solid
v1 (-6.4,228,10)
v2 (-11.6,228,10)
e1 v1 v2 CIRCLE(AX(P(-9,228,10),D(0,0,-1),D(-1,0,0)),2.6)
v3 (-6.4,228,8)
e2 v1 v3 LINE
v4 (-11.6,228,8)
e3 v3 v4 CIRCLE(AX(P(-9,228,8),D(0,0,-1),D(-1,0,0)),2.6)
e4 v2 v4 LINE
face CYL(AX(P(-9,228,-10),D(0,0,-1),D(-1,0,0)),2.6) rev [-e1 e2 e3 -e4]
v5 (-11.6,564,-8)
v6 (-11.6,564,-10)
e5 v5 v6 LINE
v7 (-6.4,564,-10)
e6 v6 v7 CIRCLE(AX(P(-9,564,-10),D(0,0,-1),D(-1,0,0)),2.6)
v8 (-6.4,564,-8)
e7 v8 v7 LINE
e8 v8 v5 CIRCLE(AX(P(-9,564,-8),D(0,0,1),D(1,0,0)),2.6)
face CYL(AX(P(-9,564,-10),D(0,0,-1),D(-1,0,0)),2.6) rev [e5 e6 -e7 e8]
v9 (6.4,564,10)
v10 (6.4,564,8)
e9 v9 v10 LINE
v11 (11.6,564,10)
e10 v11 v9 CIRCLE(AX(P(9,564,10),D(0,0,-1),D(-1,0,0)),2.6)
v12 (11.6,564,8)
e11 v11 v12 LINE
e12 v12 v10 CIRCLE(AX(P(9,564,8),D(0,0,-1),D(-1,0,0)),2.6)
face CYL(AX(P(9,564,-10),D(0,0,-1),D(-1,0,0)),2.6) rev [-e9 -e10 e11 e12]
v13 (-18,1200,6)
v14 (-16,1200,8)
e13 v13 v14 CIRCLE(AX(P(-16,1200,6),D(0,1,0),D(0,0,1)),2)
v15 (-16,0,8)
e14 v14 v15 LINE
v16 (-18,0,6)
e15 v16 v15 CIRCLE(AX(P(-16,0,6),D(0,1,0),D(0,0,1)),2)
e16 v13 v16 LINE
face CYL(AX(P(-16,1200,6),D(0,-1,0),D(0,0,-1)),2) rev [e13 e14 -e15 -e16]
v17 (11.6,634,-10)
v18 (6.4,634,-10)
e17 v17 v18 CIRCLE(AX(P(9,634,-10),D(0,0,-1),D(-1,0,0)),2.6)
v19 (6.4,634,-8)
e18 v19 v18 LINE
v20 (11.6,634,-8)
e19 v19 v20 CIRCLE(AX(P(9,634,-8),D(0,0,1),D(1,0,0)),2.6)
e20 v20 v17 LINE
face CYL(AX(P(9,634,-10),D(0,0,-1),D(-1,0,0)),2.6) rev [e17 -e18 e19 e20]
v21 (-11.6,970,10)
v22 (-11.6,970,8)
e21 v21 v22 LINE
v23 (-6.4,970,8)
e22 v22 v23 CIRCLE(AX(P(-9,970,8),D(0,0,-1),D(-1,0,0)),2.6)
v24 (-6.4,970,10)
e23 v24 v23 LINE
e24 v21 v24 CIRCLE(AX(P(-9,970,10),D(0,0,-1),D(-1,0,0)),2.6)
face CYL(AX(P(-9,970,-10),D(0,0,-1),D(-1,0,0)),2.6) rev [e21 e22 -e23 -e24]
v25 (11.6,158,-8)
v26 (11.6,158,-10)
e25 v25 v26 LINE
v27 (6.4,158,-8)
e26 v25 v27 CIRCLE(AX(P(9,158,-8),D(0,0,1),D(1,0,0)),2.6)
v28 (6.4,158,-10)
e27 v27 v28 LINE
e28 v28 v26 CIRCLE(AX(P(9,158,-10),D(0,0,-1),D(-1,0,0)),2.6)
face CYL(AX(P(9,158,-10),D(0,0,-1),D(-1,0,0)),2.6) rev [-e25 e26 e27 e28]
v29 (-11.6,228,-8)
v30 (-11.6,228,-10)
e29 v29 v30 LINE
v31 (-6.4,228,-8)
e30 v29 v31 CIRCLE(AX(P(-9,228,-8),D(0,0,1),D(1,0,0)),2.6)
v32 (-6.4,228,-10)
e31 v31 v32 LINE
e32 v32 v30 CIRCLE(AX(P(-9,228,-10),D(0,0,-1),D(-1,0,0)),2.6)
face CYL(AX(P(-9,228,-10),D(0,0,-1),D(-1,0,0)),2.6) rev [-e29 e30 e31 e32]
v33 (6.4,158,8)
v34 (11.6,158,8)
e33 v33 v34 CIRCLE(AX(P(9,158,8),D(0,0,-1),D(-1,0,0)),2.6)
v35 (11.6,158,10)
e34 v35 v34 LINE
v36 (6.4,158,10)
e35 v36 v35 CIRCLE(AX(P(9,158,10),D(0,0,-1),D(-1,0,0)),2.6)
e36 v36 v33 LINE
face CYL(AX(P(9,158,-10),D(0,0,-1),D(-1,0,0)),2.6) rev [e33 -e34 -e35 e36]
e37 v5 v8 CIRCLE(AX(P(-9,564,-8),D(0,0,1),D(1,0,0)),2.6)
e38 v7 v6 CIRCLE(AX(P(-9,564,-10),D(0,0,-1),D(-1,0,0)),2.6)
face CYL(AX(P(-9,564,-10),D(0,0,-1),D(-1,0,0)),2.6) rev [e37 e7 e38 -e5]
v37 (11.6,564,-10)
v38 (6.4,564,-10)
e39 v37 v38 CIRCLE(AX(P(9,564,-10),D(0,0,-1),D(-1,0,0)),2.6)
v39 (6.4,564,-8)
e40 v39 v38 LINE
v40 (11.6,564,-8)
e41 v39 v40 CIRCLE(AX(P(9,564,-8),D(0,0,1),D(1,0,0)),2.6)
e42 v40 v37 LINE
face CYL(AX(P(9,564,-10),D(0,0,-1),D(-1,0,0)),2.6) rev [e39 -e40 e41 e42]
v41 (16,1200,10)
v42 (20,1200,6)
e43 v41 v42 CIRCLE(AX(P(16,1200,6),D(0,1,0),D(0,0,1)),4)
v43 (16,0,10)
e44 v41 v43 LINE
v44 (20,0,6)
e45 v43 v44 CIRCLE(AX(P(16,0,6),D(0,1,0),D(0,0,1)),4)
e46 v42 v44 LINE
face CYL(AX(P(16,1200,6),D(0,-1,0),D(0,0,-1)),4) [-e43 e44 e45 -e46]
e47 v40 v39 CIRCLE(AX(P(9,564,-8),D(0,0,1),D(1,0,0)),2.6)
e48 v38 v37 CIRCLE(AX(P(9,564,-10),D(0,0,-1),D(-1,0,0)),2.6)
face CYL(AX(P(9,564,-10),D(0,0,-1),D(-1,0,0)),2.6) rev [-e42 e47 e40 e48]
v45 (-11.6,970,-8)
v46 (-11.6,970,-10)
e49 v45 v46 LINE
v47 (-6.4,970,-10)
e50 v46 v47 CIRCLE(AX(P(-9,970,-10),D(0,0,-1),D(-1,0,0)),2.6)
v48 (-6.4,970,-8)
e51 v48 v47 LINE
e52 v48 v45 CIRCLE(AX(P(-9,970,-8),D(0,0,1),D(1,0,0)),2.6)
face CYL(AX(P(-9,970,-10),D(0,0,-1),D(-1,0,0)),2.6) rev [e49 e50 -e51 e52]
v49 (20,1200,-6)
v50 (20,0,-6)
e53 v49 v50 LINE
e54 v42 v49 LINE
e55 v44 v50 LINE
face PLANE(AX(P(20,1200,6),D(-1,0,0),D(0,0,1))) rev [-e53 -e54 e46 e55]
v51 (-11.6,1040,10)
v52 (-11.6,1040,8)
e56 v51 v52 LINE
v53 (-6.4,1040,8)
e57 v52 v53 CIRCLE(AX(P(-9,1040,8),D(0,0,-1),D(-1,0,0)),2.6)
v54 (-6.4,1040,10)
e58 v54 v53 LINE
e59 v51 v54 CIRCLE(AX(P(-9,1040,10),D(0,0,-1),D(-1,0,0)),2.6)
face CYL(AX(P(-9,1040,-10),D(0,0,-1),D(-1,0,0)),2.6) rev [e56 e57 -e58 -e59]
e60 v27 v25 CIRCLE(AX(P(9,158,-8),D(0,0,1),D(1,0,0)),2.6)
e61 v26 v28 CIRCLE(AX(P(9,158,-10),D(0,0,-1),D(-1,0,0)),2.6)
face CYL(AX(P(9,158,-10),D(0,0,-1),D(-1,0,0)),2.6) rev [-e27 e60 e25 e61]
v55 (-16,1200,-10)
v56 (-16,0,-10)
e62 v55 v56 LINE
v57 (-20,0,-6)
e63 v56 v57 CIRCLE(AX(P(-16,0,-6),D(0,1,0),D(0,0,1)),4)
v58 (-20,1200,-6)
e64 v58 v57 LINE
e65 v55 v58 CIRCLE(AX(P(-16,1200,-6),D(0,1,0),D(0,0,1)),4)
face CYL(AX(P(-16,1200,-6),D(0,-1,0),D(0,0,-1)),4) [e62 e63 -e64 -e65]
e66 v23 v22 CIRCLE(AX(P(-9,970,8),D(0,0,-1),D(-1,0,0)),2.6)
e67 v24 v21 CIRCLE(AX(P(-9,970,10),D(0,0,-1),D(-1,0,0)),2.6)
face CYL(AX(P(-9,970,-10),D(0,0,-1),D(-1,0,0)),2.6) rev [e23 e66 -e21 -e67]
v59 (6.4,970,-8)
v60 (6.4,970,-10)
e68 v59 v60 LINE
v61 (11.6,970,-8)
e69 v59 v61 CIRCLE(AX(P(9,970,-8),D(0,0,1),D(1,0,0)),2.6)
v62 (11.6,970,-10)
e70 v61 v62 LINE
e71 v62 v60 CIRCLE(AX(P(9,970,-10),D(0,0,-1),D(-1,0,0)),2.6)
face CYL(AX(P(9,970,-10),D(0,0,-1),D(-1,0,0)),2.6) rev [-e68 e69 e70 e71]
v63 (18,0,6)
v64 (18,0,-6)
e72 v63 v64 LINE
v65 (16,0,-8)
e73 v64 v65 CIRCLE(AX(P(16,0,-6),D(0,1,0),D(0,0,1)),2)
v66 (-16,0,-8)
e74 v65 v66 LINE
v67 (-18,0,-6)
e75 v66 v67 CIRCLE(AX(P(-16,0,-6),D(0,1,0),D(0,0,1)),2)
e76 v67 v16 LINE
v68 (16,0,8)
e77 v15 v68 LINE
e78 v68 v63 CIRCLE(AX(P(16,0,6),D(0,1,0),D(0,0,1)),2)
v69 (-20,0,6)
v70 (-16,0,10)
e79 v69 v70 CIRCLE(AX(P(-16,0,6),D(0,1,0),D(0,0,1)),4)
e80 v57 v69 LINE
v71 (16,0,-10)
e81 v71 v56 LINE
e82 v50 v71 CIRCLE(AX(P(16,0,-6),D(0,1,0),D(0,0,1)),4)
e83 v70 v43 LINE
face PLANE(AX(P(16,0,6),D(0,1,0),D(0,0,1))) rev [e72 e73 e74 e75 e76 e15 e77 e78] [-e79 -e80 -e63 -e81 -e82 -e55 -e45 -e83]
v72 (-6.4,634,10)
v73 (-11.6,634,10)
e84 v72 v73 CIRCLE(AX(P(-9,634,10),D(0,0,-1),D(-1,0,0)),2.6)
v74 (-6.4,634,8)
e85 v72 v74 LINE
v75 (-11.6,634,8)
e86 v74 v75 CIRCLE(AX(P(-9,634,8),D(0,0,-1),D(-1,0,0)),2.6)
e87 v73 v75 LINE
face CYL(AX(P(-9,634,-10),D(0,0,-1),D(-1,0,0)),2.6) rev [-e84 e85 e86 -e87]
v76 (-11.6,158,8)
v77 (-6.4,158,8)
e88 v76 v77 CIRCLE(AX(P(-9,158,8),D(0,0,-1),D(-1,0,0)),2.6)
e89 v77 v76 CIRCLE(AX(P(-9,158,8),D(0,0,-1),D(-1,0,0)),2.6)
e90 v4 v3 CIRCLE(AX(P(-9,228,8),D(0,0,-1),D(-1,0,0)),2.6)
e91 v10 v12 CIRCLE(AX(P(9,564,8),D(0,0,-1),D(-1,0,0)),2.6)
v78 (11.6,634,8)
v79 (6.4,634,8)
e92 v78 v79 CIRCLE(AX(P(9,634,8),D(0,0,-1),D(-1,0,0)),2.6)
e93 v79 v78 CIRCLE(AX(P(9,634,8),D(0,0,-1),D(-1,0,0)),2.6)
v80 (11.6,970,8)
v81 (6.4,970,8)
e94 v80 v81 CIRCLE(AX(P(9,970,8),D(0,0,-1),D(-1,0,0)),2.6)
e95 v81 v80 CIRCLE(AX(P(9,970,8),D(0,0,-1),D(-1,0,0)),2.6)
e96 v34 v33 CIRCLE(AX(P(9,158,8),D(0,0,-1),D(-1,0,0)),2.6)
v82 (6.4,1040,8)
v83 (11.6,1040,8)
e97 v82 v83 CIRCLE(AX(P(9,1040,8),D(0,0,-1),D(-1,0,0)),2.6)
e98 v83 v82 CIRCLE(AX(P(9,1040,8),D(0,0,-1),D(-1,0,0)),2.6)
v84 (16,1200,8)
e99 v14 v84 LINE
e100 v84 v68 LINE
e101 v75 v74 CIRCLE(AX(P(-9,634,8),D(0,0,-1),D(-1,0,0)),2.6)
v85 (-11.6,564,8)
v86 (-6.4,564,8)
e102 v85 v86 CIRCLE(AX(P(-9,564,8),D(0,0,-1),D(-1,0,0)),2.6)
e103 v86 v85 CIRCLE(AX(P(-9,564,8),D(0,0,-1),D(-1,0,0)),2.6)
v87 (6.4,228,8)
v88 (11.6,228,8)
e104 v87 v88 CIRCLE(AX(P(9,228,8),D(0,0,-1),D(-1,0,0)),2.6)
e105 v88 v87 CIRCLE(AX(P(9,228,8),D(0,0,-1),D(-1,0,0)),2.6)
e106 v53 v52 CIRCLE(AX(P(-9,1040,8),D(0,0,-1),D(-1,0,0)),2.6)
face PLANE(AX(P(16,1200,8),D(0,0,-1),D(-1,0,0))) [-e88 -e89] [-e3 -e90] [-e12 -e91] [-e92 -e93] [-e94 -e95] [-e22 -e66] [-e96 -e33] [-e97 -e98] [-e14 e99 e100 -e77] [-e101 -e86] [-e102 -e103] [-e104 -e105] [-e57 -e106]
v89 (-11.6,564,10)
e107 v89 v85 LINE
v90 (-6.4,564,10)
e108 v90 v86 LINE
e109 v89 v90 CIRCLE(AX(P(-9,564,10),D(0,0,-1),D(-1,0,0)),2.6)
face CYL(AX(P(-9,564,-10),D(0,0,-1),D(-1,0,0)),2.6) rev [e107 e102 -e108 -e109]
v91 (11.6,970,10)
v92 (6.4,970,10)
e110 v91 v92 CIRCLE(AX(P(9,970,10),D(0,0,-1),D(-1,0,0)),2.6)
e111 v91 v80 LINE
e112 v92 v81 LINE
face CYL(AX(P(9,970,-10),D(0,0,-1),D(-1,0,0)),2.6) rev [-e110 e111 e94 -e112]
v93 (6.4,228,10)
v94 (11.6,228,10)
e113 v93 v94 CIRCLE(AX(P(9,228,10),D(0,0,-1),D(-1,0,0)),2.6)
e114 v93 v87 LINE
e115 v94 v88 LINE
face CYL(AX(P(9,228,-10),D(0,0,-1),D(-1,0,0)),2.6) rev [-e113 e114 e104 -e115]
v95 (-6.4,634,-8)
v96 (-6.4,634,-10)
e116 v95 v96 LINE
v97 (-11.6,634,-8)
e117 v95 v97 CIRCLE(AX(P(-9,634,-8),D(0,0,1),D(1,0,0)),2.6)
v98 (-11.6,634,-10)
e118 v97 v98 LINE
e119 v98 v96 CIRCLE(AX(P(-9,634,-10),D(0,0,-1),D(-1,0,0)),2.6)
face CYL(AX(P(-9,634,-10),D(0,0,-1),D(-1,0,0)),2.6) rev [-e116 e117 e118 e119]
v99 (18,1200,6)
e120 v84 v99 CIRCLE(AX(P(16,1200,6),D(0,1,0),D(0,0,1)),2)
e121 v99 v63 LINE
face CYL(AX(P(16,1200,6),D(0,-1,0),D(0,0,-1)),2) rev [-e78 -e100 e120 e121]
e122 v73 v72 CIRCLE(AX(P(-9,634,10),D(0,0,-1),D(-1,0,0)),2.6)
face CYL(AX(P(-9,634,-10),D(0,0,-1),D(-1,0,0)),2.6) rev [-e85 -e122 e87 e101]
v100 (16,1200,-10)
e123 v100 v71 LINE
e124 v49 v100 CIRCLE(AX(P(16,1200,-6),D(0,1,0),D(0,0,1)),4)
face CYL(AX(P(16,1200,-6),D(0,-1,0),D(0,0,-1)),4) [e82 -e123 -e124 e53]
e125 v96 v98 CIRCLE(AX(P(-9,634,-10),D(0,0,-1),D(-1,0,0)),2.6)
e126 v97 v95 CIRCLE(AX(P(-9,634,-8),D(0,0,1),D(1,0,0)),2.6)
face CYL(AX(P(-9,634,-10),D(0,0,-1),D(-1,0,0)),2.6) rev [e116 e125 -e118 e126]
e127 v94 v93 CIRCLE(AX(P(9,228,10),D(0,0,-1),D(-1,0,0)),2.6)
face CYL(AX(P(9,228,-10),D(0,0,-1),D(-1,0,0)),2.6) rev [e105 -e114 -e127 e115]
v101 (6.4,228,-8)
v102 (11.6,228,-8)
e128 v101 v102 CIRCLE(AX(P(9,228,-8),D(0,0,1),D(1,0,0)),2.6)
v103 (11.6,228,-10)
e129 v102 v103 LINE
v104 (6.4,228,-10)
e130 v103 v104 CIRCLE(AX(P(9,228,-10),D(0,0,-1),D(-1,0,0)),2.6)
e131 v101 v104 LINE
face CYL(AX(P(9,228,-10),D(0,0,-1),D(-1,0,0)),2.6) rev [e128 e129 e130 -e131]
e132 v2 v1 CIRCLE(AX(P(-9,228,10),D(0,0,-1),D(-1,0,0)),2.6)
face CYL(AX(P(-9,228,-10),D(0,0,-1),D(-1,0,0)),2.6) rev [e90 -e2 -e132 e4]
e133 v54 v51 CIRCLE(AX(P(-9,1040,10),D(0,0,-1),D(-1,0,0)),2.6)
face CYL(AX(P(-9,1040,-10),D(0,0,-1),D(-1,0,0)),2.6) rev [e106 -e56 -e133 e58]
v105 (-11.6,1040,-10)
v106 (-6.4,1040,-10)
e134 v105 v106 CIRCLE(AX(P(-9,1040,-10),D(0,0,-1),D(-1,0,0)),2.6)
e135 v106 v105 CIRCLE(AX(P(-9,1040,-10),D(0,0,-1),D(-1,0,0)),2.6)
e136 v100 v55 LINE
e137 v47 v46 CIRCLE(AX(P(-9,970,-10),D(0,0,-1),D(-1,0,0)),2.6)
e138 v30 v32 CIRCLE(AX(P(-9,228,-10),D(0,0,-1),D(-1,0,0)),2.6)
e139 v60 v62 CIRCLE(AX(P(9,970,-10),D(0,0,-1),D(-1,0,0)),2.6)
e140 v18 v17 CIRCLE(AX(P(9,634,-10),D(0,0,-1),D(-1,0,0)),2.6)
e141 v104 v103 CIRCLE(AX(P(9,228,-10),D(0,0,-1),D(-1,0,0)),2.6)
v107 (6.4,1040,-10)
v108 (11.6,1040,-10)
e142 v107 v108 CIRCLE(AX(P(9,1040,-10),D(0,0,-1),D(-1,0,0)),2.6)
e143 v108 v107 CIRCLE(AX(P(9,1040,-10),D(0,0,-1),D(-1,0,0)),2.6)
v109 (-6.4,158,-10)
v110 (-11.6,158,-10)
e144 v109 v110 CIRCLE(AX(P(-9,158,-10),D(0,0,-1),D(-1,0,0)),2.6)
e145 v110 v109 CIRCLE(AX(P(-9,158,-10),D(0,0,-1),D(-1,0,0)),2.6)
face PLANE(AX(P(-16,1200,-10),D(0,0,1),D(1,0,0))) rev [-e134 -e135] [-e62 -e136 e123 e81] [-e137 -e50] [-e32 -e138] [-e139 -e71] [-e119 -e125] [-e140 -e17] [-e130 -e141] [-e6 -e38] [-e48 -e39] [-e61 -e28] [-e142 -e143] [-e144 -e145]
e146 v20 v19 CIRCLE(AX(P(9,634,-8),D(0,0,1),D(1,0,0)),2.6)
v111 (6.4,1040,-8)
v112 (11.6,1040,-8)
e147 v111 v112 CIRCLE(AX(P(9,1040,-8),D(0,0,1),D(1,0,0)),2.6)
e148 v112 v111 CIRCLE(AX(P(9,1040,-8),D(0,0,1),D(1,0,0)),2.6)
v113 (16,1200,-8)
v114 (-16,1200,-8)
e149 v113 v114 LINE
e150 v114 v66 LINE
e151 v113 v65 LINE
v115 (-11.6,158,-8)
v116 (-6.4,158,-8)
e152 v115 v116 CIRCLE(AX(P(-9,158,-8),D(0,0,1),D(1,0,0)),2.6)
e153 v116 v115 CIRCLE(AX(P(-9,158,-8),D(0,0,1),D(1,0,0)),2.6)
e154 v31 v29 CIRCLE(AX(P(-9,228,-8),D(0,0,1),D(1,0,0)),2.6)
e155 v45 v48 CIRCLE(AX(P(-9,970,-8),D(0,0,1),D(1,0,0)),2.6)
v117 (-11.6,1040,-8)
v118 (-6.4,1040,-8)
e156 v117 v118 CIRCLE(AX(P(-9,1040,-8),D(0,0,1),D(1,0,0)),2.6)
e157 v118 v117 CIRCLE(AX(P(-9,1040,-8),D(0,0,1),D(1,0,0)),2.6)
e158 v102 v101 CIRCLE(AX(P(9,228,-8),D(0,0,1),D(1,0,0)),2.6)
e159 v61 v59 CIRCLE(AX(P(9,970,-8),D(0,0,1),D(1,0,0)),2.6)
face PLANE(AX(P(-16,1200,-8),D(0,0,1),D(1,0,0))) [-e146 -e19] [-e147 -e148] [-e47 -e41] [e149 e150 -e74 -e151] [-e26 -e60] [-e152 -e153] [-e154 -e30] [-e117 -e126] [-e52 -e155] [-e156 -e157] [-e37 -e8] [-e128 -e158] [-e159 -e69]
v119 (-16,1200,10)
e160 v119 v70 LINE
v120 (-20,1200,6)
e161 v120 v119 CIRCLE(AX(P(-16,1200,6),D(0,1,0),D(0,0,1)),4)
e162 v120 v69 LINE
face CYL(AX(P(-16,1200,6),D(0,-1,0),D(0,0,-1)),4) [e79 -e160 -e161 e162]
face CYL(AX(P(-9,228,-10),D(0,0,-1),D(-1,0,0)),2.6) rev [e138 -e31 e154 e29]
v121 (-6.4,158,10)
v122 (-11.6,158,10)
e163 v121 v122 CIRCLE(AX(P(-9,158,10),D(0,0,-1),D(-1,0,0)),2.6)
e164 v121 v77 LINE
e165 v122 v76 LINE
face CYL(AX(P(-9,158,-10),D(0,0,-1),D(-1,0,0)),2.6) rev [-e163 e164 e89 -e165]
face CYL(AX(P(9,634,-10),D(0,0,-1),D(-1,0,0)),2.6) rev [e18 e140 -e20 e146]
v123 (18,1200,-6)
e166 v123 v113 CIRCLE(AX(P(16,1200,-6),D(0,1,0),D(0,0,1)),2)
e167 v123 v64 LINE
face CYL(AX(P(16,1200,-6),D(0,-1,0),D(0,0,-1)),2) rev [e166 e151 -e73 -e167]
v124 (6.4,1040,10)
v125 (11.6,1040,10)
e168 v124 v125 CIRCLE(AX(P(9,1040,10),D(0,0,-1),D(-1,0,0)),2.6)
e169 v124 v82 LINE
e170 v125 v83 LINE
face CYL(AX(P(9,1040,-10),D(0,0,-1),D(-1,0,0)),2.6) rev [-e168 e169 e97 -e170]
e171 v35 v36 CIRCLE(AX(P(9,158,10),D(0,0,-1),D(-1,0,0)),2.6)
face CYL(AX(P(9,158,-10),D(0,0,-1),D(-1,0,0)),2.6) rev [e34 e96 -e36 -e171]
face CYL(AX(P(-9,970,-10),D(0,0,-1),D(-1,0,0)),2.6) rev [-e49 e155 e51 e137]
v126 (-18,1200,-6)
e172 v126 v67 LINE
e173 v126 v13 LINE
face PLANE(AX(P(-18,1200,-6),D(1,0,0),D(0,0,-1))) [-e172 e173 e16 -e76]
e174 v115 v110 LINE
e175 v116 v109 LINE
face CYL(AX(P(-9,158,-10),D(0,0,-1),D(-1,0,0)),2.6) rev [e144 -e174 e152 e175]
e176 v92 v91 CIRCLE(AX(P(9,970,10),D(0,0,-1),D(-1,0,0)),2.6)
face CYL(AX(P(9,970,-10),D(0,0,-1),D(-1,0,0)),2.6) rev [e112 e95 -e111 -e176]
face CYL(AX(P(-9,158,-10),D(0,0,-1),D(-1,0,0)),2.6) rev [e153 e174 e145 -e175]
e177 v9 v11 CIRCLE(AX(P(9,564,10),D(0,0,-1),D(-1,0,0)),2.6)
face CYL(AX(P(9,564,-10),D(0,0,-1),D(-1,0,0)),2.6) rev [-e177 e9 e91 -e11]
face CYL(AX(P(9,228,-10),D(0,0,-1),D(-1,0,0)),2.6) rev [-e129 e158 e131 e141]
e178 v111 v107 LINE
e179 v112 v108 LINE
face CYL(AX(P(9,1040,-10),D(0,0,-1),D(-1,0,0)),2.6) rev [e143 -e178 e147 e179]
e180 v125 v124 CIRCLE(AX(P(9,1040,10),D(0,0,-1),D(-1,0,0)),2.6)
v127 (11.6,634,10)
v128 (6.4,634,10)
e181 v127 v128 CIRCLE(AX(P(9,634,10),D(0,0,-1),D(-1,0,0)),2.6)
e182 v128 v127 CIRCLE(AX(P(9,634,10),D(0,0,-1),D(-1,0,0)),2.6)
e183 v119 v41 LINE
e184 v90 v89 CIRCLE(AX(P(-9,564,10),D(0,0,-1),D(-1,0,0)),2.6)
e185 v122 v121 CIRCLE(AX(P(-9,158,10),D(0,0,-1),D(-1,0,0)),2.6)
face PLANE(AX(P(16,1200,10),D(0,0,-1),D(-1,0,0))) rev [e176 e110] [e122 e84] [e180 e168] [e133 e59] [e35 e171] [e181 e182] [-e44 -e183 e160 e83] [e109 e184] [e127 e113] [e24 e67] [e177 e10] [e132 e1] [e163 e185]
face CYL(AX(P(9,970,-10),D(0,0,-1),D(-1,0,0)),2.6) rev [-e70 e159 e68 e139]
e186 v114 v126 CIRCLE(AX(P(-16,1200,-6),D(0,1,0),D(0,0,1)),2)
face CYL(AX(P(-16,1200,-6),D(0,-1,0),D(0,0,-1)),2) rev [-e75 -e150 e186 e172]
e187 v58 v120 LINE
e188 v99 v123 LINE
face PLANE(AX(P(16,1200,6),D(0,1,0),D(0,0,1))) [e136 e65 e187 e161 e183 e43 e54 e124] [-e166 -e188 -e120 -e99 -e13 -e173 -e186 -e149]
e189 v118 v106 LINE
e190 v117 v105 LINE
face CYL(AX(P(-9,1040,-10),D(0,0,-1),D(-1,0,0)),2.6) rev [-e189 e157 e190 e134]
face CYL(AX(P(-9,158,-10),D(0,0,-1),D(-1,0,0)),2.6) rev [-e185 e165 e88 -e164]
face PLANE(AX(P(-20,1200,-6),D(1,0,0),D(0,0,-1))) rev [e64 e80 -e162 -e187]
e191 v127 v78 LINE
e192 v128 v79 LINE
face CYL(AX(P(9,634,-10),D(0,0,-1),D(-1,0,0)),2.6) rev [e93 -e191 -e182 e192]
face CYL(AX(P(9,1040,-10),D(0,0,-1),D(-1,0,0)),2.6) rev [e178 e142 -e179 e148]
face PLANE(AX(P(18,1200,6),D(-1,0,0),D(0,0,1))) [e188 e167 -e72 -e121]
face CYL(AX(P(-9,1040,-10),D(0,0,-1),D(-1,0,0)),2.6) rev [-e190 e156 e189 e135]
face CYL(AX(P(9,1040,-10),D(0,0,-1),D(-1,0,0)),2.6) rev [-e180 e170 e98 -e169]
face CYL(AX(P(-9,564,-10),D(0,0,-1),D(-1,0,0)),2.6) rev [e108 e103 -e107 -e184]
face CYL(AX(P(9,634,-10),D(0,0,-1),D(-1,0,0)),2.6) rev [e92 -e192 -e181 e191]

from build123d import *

# Parameters (mm, degrees)
F_40X20X2_1_DEPTH       = 1200
HOLE_WIZARD_5_2_5_2_1_D = 5.2
PATTERN_LINEAR_1_COUNT  = 3
PATTERN_LINEAR_1_PITCH  = 406


with BuildPart() as part:
    # Sketch1 → 矩型管 40X20X2(1) (new body)
    with BuildSketch(Plane.ZX):
        with BuildLine():
            Line((-6, -20), (6, -20))
            ThreePointArc((6, -20), (8.828427125, -18.828427125), (10, -16))
            Line((10, -16), (10, 16))
            ThreePointArc((10, 16), (8.828427125, 18.828427125), (6, 20))
            Line((6, 20), (-6, 20))
            ThreePointArc((-6, 20), (-8.828427125, 18.828427125), (-10, 16))
            Line((-10, 16), (-10, -16))
            ThreePointArc((-10, -16), (-8.828427125, -18.828427125), (-6, -20))
        make_face()
        with BuildLine():
            Line((-6, -18), (6, -18))
            ThreePointArc((6, -18), (7.414213562, -17.414213562), (8, -16))
            Line((8, -16), (8, 16))
            ThreePointArc((8, 16), (7.414213562, 17.414213562), (6, 18))
            Line((6, 18), (-6, 18))
            ThreePointArc((-6, 18), (-7.414213562, 17.414213562), (-8, 16))
            Line((-8, 16), (-8, -16))
            ThreePointArc((-8, -16), (-7.414213562, -17.414213562), (-6, -18))
        make_face(mode=Mode.SUBTRACT)
    extrude(amount=F_40X20X2_1_DEPTH)

    # Ø5.2 (5.2) 直径孔1 (through all)
    with Locations(Plane(origin=(0, 0, -10), x_dir=(-1, 0, 0), z_dir=(0, 0, -1))):
        with Locations((-9, 1040), (9, 1040), (9, 970), (-9, 970)):
            hole_wizard_5_2_5_2_1 = Hole(HOLE_WIZARD_5_2_5_2_1_D / 2)

    # 阵列(线性)1: Ø5.2 (5.2) 直径孔1 ×3
    with Locations(*[(0, -i * PATTERN_LINEAR_1_PITCH, 0) for i in range(1, PATTERN_LINEAR_1_COUNT)]):
        add(hole_wizard_5_2_5_2_1, mode=Mode.SUBTRACT)


solid = part.part
